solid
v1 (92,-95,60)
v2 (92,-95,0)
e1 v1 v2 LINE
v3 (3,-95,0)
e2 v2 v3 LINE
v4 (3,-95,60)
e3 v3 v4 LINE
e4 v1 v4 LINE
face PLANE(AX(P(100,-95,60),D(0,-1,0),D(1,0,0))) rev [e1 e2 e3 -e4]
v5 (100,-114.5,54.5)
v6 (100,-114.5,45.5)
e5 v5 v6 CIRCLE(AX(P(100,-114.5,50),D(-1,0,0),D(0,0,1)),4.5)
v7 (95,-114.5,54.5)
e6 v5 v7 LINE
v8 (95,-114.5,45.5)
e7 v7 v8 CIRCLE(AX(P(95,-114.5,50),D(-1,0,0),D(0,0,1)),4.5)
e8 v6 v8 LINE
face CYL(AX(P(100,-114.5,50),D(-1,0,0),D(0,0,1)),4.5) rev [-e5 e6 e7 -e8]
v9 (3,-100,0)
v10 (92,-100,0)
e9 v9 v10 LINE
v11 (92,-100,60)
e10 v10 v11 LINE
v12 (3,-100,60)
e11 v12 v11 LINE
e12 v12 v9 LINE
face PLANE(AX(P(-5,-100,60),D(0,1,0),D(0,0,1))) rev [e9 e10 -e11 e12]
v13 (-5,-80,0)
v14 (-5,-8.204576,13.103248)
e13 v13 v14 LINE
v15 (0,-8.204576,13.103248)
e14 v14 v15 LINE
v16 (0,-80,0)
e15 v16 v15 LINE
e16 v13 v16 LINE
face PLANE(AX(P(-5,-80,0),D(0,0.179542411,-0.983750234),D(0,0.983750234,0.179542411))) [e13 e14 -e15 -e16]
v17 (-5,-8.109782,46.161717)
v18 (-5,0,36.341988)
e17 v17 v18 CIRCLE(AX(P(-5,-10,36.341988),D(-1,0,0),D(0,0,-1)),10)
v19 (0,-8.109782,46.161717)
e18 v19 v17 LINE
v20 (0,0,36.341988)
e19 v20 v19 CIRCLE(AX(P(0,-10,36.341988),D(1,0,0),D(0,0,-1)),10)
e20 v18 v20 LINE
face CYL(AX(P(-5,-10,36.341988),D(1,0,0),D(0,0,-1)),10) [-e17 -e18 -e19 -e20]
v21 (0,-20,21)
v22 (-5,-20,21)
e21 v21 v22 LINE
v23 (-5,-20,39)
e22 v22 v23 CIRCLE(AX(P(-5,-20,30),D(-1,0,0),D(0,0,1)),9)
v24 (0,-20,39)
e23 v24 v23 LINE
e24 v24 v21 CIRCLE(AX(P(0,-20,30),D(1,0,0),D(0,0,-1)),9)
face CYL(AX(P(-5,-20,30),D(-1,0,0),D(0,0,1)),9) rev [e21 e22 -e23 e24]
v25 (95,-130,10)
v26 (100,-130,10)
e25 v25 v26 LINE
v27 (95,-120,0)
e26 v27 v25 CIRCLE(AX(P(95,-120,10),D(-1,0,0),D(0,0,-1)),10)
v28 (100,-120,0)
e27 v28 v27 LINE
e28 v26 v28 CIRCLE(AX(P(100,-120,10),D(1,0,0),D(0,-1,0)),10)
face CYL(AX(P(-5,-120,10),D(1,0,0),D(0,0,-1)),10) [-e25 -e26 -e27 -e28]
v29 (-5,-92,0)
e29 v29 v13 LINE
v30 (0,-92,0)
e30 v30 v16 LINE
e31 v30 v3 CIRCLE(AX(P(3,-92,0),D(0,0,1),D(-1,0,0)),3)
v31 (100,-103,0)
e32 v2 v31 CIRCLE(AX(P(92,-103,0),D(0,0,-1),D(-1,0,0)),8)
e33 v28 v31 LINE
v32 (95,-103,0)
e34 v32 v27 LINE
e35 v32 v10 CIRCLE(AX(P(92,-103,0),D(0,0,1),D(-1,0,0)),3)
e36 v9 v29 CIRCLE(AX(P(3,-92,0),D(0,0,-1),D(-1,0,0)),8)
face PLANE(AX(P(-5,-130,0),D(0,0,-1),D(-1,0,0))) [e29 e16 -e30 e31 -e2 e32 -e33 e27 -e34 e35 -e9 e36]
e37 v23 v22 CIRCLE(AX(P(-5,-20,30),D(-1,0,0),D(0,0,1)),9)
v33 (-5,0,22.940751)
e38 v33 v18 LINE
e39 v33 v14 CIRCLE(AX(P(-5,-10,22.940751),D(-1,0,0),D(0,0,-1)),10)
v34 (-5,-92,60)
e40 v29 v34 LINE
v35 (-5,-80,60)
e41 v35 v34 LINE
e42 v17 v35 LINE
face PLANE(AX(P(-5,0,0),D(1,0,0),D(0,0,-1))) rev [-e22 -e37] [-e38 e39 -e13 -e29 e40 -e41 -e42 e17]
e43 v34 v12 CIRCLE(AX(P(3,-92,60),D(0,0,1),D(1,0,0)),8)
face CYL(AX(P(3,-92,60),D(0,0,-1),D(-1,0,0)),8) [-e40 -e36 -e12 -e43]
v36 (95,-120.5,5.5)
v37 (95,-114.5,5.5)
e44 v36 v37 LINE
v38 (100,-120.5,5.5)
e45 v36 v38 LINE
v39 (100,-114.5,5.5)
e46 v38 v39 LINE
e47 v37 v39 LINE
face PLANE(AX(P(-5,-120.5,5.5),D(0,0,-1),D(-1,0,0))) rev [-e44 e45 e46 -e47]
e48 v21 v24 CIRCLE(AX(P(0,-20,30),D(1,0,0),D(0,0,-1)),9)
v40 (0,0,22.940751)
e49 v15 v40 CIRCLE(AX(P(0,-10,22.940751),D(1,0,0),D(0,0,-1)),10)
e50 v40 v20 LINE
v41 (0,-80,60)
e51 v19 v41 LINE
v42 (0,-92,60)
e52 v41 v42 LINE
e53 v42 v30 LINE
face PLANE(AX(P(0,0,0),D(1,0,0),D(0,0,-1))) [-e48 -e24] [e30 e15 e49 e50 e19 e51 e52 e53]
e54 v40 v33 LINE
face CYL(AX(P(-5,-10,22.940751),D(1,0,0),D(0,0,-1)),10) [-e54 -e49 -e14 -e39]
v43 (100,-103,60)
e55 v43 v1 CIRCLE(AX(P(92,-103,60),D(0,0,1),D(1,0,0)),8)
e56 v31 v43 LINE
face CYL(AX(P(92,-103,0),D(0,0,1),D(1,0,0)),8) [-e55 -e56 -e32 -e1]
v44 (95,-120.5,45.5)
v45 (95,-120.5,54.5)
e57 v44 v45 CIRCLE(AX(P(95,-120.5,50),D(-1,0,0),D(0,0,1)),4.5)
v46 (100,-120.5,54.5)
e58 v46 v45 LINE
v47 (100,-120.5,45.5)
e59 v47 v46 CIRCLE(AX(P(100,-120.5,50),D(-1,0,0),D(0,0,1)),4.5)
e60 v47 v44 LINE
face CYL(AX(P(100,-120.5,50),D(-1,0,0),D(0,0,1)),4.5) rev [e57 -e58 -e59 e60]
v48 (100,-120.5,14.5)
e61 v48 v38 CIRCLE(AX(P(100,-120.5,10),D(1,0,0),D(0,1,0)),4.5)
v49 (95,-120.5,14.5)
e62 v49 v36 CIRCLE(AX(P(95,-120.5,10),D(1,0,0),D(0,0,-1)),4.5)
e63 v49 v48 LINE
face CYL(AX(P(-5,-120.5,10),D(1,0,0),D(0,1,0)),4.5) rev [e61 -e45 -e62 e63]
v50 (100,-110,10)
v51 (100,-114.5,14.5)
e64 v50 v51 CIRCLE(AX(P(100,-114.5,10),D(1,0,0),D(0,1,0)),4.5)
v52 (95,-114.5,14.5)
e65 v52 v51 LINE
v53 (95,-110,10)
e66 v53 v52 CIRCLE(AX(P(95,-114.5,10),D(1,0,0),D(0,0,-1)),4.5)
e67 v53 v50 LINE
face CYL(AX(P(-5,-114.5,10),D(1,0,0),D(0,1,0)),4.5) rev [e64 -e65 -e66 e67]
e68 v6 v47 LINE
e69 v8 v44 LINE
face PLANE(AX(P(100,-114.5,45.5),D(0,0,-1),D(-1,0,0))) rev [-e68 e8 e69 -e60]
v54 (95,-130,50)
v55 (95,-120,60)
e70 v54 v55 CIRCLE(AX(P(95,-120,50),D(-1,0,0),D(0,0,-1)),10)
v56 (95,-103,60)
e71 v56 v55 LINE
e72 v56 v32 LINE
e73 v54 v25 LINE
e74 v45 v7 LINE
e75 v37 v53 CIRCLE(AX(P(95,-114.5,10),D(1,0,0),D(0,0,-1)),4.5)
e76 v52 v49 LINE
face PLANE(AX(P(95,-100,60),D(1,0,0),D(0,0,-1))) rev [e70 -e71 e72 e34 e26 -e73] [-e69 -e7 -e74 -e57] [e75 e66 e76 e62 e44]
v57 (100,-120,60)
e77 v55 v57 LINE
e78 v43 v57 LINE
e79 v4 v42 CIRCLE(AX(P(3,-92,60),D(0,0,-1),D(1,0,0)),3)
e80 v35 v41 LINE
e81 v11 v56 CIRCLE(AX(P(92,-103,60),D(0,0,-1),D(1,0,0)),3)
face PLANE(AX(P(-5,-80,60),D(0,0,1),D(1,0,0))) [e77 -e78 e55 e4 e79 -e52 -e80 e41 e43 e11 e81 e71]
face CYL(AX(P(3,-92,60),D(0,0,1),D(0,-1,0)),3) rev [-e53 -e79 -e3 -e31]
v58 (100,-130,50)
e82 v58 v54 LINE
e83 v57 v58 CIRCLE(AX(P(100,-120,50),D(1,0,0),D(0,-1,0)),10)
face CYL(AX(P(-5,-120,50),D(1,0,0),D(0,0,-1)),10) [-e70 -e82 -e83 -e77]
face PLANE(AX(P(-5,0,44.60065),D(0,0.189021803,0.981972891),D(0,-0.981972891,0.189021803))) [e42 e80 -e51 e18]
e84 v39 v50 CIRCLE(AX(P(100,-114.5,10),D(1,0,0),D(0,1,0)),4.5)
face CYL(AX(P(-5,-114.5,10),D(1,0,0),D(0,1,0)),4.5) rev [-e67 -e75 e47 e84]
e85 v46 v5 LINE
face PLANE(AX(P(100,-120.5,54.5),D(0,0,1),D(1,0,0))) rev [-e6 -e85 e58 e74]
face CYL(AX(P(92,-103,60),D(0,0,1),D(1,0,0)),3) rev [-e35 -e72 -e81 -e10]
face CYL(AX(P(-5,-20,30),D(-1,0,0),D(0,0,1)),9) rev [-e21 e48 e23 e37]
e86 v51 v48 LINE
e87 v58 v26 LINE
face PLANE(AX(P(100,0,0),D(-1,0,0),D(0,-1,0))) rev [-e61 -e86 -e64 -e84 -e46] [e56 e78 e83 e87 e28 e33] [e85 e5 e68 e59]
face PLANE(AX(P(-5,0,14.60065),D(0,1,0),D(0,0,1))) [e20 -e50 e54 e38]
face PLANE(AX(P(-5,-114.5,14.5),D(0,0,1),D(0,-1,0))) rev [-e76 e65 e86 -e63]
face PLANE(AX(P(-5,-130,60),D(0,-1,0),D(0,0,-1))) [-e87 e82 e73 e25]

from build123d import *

# Parameters (mm, degrees)
BOSS_EXTRUDE1_DEPTH            = 5
SKETCH2_W                      = 60
SKETCH2_H                      = 35
BOSS_EXTRUDE2_DEPTH            = 100
SKETCH3_W                      = 100
SKETCH3_H                      = 30
CUT_EXTRUDE1_DEPTH             = 175.642491966
CUT_EXTRUDE2_DEPTH             = 175.642491966
CUT_EXTRUDE3_DEPTH             = 178.552809046
F_18_0_18_DIAMETER_HOLE1_D     = 18
F_18_0_18_DIAMETER_HOLE1_DEPTH = 105
FILLET1_R                      = 3
FILLET2_R                      = 8
FILLET3_R                      = 10


with BuildPart() as part:
    # Sketch1 → Boss-Extrude1 (new body)
    with BuildSketch(Plane(origin=(0, 0, 0), x_dir=(0, 0, -1), z_dir=(1, 0, 0))):
        Polygon((0, -80), (-14.600649986, 0), (-44.600649986, 0), (-60, -80), (-60, -130), (0, -130), align=None)
    extrude(amount=-BOSS_EXTRUDE1_DEPTH)

    # Sketch2 → Boss-Extrude2 (add)
    with BuildSketch(Plane(origin=(0, 0, 0), x_dir=(0, 0, -1), z_dir=(1, 0, 0))):
        with Locations((-30, -112.5)):
            Rectangle(SKETCH2_W, SKETCH2_H)
    extrude(amount=BOSS_EXTRUDE2_DEPTH)

    # Sketch3 → Cut-Extrude1 (cut, through all)
    with BuildSketch(Plane(origin=(0, 0, 0), x_dir=(-1, 0, 0), z_dir=(0, 0, -1))):
        with Locations((-45, -115)):
            Rectangle(SKETCH3_W, SKETCH3_H)
    extrude(amount=-CUT_EXTRUDE1_DEPTH, mode=Mode.SUBTRACT)

    # Sketch4 → Cut-Extrude2 (cut, through all)
    with BuildSketch(Plane.ZY.offset(-95)):
        with BuildLine():
            Line((54.5, -120.5), (54.5, -114.5))
            ThreePointArc((54.5, -114.5), (50, -110), (45.5, -114.5))
            Line((45.5, -114.5), (45.5, -120.5))
            ThreePointArc((45.5, -120.5), (50, -125), (54.5, -120.5))
        make_face()
    extrude(amount=-CUT_EXTRUDE2_DEPTH, mode=Mode.SUBTRACT)

    # Sketch5 → Cut-Extrude3 (cut, through all)
    with BuildSketch(Plane(origin=(100, 0, 0), x_dir=(0, 0, -1), z_dir=(1, 0, 0))):
        with BuildLine():
            Line((-14.5, -114.5), (-14.5, -120.5))
            ThreePointArc((-14.5, -120.5), (-10, -125), (-5.5, -120.5))
            Line((-5.5, -120.5), (-5.5, -114.5))
            ThreePointArc((-5.5, -114.5), (-10, -110), (-14.5, -114.5))
        make_face()
    extrude(amount=-CUT_EXTRUDE3_DEPTH, mode=Mode.SUBTRACT)

    # Ø18.0 (18) Diameter Hole1
    with Locations(Plane.ZY.offset(5)):
        with Locations((30, -20)):
            Hole(F_18_0_18_DIAMETER_HOLE1_D / 2, depth=F_18_0_18_DIAMETER_HOLE1_DEPTH)

    # Fillet1
    fillet1_edges = [part.edges().sort_by_distance(p)[0] for p in [
        (0, -95, 30),
        (95, -100, 30),
    ]]
    fillet(fillet1_edges, radius=FILLET1_R)

    # Fillet2
    fillet2_edges = [part.edges().sort_by_distance(p)[0] for p in [
        (100, -95, 30),
        (-5, -100, 30),
    ]]
    fillet(fillet2_edges, radius=FILLET2_R)

    # Fillet3
    fillet3_edges = [part.edges().sort_by_distance(p)[0] for p in [
        (-2.5, 0, 44.600649986),
        (-2.5, 0, 14.600649986),
        (97.5, -130, 60),
        (97.5, -130, 0),
    ]]
    fillet(fillet3_edges, radius=FILLET3_R)


solid = part.part
